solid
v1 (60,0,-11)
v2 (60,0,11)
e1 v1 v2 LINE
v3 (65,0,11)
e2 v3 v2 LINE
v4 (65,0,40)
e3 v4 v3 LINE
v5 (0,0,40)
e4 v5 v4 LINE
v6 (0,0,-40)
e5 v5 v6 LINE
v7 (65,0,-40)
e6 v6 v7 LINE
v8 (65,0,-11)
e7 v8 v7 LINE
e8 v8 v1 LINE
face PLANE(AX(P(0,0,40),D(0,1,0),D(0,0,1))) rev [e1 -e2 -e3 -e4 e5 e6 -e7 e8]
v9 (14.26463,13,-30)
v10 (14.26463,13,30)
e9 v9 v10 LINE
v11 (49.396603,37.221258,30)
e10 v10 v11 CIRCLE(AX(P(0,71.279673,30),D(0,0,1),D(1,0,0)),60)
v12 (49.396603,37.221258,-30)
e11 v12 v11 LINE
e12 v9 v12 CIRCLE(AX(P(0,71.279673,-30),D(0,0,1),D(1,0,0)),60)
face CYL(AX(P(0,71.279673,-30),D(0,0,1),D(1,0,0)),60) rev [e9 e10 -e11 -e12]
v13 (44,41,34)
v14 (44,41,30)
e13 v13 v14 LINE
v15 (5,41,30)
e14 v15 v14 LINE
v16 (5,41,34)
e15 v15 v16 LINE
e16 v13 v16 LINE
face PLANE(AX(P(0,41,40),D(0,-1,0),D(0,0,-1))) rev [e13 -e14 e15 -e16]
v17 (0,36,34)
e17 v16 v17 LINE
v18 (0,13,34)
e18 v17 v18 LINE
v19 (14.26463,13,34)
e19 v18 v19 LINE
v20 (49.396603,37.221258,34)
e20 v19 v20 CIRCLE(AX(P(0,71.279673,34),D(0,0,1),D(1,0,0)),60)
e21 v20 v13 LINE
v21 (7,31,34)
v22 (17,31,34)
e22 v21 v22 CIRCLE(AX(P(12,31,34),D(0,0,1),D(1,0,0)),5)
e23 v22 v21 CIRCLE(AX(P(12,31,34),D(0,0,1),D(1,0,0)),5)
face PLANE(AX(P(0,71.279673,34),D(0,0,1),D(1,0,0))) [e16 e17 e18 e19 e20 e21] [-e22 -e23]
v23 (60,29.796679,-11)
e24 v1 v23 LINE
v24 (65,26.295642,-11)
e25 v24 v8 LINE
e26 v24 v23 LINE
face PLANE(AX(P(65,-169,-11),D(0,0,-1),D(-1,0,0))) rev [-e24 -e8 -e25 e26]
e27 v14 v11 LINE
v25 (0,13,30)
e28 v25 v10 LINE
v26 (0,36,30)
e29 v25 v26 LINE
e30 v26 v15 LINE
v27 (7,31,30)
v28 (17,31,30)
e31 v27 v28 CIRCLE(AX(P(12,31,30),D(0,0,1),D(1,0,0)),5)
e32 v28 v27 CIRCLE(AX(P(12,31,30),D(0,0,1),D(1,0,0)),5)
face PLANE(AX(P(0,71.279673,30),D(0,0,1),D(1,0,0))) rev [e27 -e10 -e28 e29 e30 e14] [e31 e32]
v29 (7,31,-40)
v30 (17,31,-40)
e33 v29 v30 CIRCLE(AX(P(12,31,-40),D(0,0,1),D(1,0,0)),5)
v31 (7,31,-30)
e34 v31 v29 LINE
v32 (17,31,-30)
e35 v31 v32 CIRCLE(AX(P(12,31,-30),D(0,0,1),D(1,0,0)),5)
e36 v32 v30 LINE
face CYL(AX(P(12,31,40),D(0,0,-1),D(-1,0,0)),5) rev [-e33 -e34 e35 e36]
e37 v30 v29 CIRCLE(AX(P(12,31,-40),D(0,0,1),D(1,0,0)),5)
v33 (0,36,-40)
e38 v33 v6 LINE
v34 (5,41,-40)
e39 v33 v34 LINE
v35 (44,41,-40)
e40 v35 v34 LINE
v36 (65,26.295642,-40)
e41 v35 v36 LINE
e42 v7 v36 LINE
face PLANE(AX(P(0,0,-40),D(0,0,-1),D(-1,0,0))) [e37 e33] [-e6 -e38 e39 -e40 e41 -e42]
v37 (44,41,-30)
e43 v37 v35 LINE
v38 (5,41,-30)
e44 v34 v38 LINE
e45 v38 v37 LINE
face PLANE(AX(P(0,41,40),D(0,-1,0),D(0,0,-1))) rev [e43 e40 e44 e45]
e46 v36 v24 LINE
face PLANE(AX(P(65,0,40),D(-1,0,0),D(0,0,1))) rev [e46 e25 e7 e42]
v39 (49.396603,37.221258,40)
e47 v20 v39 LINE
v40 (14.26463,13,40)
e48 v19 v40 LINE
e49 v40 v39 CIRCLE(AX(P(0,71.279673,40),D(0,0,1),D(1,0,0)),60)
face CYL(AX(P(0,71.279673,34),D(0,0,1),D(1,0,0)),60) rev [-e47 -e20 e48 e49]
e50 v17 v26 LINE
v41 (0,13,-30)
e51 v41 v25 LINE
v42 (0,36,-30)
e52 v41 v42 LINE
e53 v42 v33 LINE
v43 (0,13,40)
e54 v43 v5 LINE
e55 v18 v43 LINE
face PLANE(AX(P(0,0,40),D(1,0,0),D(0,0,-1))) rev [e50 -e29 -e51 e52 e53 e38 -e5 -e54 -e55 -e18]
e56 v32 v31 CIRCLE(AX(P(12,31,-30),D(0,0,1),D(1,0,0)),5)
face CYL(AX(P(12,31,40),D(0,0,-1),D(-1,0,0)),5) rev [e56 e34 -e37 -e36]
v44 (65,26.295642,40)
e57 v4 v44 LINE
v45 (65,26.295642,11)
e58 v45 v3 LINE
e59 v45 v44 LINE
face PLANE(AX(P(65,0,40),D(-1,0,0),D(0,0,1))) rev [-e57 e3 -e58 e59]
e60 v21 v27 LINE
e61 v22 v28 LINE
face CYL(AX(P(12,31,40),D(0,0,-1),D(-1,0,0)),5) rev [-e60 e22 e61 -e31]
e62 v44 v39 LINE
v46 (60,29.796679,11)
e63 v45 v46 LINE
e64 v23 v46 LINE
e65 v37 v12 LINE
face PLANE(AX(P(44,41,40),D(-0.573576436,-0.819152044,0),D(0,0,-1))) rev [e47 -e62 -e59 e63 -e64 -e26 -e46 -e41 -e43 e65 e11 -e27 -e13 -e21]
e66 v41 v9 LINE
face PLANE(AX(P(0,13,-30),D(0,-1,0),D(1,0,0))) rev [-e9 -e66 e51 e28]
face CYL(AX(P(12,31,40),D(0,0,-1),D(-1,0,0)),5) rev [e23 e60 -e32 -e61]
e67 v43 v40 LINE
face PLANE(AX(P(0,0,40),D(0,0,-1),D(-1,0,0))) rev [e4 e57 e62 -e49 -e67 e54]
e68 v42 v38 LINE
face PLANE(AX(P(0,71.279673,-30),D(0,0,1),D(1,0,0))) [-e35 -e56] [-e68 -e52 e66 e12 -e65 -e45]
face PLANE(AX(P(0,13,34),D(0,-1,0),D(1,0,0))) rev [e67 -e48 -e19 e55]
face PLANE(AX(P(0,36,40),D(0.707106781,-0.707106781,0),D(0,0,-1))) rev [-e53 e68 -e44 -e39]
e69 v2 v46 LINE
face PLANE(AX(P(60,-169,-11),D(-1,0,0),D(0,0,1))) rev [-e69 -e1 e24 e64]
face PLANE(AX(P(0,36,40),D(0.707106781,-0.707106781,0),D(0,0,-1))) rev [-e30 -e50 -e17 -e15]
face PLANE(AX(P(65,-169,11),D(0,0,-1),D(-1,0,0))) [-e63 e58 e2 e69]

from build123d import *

# Parameters (mm, degrees)
BLOCK_PROFILE_SKETCH_W         = 65
BLOCK_PROFILE_SKETCH_H         = 41
BLOCK_PROFILE_SKETCH_R         = 5
BLOCK_BODY_80MM_DEPTH          = 40
EDGE_CHAMFER_5MM_SIZE          = 5
TOP_CHAMFER_21MM_X_35DEG_SIZE  = 21
TOP_CHAMFER_21MM_X_35DEG_SIZE2 = 14.704358302
TOP_RECESS_CUT_6MM_DEPTH       = 6
LUG_GAP_CUT_60MM_DEPTH         = 60
THROUGH_SLOT_SKETCH_W          = 5
THROUGH_SLOT_SKETCH_H          = 22
THROUGH_SLOT_CUT_DEPTH         = 210


with BuildPart() as part:
    # Block Profile Sketch → Block Body 80mm (new, symmetric)
    with BuildSketch(Plane.XY):
        with Locations((32.5, 20.5)):
            Rectangle(BLOCK_PROFILE_SKETCH_W, BLOCK_PROFILE_SKETCH_H)
        with Locations((12, 31)):
            Circle(BLOCK_PROFILE_SKETCH_R, mode=Mode.SUBTRACT)
    extrude(amount=BLOCK_BODY_80MM_DEPTH, both=True)

    # Edge Chamfer 5mm
    edge_chamfer_5mm_edges = [part.edges().sort_by_distance(p)[0] for p in [
        (0, 41, 0),
    ]]
    chamfer(edge_chamfer_5mm_edges, length=EDGE_CHAMFER_5MM_SIZE)

    # Top Chamfer 21mm x 35deg
    top_chamfer_21mm_x_35deg_edges = [part.edges().sort_by_distance(p)[0] for p in [
        (65, 41, 0),
    ]]
    top_chamfer_21mm_x_35deg_side = [part.faces().sort_by_distance(p)[0] for p in [
        (35, 41, 0),
    ]]
    chamfer(top_chamfer_21mm_x_35deg_edges, length=TOP_CHAMFER_21MM_X_35DEG_SIZE, length2=TOP_CHAMFER_21MM_X_35DEG_SIZE2, reference=top_chamfer_21mm_x_35deg_side[0])

    # Top Recess Sketch → Top Recess Cut 6mm (cut)
    with BuildSketch(Plane.XY.offset(40)):
        with BuildLine():
            Line((0, 13), (14.264629746, 13))
            ThreePointArc((14.264629746, 13), (34.056650789, 21.881854304), (49.396602602, 37.221258177))
            Line((49.396602602, 37.221258177), (44, 41))
            Line((44, 41), (5, 41))
            Line((5, 41), (0, 36))
            Line((0, 36), (0, 13))
        make_face()
    extrude(amount=-TOP_RECESS_CUT_6MM_DEPTH, mode=Mode.SUBTRACT)

    # Lug Gap Sketch → Lug Gap Cut 60mm (cut)
    with BuildSketch(Plane.XY.offset(30)):
        with BuildLine():
            Line((0, 13), (0, 36))
            Line((0, 36), (5, 41))
            Line((5, 41), (44, 41))
            Line((44, 41), (49.396602602, 37.221258177))
            ThreePointArc((49.396602602, 37.221258177), (34.056650789, 21.881854304), (14.264629746, 13))
            Line((14.264629746, 13), (0, 13))
        make_face()
    extrude(amount=-LUG_GAP_CUT_60MM_DEPTH, mode=Mode.SUBTRACT)

    # Through Slot Sketch → Through Slot Cut (cut)
    with BuildSketch(Plane(origin=(0, 41, 0), x_dir=(1, 0, 0), z_dir=(0, 1, 0))):
        with Locations((62.5, 0)):
            Rectangle(THROUGH_SLOT_SKETCH_W, THROUGH_SLOT_SKETCH_H)
    extrude(amount=-THROUGH_SLOT_CUT_DEPTH, mode=Mode.SUBTRACT)


solid = part.part
